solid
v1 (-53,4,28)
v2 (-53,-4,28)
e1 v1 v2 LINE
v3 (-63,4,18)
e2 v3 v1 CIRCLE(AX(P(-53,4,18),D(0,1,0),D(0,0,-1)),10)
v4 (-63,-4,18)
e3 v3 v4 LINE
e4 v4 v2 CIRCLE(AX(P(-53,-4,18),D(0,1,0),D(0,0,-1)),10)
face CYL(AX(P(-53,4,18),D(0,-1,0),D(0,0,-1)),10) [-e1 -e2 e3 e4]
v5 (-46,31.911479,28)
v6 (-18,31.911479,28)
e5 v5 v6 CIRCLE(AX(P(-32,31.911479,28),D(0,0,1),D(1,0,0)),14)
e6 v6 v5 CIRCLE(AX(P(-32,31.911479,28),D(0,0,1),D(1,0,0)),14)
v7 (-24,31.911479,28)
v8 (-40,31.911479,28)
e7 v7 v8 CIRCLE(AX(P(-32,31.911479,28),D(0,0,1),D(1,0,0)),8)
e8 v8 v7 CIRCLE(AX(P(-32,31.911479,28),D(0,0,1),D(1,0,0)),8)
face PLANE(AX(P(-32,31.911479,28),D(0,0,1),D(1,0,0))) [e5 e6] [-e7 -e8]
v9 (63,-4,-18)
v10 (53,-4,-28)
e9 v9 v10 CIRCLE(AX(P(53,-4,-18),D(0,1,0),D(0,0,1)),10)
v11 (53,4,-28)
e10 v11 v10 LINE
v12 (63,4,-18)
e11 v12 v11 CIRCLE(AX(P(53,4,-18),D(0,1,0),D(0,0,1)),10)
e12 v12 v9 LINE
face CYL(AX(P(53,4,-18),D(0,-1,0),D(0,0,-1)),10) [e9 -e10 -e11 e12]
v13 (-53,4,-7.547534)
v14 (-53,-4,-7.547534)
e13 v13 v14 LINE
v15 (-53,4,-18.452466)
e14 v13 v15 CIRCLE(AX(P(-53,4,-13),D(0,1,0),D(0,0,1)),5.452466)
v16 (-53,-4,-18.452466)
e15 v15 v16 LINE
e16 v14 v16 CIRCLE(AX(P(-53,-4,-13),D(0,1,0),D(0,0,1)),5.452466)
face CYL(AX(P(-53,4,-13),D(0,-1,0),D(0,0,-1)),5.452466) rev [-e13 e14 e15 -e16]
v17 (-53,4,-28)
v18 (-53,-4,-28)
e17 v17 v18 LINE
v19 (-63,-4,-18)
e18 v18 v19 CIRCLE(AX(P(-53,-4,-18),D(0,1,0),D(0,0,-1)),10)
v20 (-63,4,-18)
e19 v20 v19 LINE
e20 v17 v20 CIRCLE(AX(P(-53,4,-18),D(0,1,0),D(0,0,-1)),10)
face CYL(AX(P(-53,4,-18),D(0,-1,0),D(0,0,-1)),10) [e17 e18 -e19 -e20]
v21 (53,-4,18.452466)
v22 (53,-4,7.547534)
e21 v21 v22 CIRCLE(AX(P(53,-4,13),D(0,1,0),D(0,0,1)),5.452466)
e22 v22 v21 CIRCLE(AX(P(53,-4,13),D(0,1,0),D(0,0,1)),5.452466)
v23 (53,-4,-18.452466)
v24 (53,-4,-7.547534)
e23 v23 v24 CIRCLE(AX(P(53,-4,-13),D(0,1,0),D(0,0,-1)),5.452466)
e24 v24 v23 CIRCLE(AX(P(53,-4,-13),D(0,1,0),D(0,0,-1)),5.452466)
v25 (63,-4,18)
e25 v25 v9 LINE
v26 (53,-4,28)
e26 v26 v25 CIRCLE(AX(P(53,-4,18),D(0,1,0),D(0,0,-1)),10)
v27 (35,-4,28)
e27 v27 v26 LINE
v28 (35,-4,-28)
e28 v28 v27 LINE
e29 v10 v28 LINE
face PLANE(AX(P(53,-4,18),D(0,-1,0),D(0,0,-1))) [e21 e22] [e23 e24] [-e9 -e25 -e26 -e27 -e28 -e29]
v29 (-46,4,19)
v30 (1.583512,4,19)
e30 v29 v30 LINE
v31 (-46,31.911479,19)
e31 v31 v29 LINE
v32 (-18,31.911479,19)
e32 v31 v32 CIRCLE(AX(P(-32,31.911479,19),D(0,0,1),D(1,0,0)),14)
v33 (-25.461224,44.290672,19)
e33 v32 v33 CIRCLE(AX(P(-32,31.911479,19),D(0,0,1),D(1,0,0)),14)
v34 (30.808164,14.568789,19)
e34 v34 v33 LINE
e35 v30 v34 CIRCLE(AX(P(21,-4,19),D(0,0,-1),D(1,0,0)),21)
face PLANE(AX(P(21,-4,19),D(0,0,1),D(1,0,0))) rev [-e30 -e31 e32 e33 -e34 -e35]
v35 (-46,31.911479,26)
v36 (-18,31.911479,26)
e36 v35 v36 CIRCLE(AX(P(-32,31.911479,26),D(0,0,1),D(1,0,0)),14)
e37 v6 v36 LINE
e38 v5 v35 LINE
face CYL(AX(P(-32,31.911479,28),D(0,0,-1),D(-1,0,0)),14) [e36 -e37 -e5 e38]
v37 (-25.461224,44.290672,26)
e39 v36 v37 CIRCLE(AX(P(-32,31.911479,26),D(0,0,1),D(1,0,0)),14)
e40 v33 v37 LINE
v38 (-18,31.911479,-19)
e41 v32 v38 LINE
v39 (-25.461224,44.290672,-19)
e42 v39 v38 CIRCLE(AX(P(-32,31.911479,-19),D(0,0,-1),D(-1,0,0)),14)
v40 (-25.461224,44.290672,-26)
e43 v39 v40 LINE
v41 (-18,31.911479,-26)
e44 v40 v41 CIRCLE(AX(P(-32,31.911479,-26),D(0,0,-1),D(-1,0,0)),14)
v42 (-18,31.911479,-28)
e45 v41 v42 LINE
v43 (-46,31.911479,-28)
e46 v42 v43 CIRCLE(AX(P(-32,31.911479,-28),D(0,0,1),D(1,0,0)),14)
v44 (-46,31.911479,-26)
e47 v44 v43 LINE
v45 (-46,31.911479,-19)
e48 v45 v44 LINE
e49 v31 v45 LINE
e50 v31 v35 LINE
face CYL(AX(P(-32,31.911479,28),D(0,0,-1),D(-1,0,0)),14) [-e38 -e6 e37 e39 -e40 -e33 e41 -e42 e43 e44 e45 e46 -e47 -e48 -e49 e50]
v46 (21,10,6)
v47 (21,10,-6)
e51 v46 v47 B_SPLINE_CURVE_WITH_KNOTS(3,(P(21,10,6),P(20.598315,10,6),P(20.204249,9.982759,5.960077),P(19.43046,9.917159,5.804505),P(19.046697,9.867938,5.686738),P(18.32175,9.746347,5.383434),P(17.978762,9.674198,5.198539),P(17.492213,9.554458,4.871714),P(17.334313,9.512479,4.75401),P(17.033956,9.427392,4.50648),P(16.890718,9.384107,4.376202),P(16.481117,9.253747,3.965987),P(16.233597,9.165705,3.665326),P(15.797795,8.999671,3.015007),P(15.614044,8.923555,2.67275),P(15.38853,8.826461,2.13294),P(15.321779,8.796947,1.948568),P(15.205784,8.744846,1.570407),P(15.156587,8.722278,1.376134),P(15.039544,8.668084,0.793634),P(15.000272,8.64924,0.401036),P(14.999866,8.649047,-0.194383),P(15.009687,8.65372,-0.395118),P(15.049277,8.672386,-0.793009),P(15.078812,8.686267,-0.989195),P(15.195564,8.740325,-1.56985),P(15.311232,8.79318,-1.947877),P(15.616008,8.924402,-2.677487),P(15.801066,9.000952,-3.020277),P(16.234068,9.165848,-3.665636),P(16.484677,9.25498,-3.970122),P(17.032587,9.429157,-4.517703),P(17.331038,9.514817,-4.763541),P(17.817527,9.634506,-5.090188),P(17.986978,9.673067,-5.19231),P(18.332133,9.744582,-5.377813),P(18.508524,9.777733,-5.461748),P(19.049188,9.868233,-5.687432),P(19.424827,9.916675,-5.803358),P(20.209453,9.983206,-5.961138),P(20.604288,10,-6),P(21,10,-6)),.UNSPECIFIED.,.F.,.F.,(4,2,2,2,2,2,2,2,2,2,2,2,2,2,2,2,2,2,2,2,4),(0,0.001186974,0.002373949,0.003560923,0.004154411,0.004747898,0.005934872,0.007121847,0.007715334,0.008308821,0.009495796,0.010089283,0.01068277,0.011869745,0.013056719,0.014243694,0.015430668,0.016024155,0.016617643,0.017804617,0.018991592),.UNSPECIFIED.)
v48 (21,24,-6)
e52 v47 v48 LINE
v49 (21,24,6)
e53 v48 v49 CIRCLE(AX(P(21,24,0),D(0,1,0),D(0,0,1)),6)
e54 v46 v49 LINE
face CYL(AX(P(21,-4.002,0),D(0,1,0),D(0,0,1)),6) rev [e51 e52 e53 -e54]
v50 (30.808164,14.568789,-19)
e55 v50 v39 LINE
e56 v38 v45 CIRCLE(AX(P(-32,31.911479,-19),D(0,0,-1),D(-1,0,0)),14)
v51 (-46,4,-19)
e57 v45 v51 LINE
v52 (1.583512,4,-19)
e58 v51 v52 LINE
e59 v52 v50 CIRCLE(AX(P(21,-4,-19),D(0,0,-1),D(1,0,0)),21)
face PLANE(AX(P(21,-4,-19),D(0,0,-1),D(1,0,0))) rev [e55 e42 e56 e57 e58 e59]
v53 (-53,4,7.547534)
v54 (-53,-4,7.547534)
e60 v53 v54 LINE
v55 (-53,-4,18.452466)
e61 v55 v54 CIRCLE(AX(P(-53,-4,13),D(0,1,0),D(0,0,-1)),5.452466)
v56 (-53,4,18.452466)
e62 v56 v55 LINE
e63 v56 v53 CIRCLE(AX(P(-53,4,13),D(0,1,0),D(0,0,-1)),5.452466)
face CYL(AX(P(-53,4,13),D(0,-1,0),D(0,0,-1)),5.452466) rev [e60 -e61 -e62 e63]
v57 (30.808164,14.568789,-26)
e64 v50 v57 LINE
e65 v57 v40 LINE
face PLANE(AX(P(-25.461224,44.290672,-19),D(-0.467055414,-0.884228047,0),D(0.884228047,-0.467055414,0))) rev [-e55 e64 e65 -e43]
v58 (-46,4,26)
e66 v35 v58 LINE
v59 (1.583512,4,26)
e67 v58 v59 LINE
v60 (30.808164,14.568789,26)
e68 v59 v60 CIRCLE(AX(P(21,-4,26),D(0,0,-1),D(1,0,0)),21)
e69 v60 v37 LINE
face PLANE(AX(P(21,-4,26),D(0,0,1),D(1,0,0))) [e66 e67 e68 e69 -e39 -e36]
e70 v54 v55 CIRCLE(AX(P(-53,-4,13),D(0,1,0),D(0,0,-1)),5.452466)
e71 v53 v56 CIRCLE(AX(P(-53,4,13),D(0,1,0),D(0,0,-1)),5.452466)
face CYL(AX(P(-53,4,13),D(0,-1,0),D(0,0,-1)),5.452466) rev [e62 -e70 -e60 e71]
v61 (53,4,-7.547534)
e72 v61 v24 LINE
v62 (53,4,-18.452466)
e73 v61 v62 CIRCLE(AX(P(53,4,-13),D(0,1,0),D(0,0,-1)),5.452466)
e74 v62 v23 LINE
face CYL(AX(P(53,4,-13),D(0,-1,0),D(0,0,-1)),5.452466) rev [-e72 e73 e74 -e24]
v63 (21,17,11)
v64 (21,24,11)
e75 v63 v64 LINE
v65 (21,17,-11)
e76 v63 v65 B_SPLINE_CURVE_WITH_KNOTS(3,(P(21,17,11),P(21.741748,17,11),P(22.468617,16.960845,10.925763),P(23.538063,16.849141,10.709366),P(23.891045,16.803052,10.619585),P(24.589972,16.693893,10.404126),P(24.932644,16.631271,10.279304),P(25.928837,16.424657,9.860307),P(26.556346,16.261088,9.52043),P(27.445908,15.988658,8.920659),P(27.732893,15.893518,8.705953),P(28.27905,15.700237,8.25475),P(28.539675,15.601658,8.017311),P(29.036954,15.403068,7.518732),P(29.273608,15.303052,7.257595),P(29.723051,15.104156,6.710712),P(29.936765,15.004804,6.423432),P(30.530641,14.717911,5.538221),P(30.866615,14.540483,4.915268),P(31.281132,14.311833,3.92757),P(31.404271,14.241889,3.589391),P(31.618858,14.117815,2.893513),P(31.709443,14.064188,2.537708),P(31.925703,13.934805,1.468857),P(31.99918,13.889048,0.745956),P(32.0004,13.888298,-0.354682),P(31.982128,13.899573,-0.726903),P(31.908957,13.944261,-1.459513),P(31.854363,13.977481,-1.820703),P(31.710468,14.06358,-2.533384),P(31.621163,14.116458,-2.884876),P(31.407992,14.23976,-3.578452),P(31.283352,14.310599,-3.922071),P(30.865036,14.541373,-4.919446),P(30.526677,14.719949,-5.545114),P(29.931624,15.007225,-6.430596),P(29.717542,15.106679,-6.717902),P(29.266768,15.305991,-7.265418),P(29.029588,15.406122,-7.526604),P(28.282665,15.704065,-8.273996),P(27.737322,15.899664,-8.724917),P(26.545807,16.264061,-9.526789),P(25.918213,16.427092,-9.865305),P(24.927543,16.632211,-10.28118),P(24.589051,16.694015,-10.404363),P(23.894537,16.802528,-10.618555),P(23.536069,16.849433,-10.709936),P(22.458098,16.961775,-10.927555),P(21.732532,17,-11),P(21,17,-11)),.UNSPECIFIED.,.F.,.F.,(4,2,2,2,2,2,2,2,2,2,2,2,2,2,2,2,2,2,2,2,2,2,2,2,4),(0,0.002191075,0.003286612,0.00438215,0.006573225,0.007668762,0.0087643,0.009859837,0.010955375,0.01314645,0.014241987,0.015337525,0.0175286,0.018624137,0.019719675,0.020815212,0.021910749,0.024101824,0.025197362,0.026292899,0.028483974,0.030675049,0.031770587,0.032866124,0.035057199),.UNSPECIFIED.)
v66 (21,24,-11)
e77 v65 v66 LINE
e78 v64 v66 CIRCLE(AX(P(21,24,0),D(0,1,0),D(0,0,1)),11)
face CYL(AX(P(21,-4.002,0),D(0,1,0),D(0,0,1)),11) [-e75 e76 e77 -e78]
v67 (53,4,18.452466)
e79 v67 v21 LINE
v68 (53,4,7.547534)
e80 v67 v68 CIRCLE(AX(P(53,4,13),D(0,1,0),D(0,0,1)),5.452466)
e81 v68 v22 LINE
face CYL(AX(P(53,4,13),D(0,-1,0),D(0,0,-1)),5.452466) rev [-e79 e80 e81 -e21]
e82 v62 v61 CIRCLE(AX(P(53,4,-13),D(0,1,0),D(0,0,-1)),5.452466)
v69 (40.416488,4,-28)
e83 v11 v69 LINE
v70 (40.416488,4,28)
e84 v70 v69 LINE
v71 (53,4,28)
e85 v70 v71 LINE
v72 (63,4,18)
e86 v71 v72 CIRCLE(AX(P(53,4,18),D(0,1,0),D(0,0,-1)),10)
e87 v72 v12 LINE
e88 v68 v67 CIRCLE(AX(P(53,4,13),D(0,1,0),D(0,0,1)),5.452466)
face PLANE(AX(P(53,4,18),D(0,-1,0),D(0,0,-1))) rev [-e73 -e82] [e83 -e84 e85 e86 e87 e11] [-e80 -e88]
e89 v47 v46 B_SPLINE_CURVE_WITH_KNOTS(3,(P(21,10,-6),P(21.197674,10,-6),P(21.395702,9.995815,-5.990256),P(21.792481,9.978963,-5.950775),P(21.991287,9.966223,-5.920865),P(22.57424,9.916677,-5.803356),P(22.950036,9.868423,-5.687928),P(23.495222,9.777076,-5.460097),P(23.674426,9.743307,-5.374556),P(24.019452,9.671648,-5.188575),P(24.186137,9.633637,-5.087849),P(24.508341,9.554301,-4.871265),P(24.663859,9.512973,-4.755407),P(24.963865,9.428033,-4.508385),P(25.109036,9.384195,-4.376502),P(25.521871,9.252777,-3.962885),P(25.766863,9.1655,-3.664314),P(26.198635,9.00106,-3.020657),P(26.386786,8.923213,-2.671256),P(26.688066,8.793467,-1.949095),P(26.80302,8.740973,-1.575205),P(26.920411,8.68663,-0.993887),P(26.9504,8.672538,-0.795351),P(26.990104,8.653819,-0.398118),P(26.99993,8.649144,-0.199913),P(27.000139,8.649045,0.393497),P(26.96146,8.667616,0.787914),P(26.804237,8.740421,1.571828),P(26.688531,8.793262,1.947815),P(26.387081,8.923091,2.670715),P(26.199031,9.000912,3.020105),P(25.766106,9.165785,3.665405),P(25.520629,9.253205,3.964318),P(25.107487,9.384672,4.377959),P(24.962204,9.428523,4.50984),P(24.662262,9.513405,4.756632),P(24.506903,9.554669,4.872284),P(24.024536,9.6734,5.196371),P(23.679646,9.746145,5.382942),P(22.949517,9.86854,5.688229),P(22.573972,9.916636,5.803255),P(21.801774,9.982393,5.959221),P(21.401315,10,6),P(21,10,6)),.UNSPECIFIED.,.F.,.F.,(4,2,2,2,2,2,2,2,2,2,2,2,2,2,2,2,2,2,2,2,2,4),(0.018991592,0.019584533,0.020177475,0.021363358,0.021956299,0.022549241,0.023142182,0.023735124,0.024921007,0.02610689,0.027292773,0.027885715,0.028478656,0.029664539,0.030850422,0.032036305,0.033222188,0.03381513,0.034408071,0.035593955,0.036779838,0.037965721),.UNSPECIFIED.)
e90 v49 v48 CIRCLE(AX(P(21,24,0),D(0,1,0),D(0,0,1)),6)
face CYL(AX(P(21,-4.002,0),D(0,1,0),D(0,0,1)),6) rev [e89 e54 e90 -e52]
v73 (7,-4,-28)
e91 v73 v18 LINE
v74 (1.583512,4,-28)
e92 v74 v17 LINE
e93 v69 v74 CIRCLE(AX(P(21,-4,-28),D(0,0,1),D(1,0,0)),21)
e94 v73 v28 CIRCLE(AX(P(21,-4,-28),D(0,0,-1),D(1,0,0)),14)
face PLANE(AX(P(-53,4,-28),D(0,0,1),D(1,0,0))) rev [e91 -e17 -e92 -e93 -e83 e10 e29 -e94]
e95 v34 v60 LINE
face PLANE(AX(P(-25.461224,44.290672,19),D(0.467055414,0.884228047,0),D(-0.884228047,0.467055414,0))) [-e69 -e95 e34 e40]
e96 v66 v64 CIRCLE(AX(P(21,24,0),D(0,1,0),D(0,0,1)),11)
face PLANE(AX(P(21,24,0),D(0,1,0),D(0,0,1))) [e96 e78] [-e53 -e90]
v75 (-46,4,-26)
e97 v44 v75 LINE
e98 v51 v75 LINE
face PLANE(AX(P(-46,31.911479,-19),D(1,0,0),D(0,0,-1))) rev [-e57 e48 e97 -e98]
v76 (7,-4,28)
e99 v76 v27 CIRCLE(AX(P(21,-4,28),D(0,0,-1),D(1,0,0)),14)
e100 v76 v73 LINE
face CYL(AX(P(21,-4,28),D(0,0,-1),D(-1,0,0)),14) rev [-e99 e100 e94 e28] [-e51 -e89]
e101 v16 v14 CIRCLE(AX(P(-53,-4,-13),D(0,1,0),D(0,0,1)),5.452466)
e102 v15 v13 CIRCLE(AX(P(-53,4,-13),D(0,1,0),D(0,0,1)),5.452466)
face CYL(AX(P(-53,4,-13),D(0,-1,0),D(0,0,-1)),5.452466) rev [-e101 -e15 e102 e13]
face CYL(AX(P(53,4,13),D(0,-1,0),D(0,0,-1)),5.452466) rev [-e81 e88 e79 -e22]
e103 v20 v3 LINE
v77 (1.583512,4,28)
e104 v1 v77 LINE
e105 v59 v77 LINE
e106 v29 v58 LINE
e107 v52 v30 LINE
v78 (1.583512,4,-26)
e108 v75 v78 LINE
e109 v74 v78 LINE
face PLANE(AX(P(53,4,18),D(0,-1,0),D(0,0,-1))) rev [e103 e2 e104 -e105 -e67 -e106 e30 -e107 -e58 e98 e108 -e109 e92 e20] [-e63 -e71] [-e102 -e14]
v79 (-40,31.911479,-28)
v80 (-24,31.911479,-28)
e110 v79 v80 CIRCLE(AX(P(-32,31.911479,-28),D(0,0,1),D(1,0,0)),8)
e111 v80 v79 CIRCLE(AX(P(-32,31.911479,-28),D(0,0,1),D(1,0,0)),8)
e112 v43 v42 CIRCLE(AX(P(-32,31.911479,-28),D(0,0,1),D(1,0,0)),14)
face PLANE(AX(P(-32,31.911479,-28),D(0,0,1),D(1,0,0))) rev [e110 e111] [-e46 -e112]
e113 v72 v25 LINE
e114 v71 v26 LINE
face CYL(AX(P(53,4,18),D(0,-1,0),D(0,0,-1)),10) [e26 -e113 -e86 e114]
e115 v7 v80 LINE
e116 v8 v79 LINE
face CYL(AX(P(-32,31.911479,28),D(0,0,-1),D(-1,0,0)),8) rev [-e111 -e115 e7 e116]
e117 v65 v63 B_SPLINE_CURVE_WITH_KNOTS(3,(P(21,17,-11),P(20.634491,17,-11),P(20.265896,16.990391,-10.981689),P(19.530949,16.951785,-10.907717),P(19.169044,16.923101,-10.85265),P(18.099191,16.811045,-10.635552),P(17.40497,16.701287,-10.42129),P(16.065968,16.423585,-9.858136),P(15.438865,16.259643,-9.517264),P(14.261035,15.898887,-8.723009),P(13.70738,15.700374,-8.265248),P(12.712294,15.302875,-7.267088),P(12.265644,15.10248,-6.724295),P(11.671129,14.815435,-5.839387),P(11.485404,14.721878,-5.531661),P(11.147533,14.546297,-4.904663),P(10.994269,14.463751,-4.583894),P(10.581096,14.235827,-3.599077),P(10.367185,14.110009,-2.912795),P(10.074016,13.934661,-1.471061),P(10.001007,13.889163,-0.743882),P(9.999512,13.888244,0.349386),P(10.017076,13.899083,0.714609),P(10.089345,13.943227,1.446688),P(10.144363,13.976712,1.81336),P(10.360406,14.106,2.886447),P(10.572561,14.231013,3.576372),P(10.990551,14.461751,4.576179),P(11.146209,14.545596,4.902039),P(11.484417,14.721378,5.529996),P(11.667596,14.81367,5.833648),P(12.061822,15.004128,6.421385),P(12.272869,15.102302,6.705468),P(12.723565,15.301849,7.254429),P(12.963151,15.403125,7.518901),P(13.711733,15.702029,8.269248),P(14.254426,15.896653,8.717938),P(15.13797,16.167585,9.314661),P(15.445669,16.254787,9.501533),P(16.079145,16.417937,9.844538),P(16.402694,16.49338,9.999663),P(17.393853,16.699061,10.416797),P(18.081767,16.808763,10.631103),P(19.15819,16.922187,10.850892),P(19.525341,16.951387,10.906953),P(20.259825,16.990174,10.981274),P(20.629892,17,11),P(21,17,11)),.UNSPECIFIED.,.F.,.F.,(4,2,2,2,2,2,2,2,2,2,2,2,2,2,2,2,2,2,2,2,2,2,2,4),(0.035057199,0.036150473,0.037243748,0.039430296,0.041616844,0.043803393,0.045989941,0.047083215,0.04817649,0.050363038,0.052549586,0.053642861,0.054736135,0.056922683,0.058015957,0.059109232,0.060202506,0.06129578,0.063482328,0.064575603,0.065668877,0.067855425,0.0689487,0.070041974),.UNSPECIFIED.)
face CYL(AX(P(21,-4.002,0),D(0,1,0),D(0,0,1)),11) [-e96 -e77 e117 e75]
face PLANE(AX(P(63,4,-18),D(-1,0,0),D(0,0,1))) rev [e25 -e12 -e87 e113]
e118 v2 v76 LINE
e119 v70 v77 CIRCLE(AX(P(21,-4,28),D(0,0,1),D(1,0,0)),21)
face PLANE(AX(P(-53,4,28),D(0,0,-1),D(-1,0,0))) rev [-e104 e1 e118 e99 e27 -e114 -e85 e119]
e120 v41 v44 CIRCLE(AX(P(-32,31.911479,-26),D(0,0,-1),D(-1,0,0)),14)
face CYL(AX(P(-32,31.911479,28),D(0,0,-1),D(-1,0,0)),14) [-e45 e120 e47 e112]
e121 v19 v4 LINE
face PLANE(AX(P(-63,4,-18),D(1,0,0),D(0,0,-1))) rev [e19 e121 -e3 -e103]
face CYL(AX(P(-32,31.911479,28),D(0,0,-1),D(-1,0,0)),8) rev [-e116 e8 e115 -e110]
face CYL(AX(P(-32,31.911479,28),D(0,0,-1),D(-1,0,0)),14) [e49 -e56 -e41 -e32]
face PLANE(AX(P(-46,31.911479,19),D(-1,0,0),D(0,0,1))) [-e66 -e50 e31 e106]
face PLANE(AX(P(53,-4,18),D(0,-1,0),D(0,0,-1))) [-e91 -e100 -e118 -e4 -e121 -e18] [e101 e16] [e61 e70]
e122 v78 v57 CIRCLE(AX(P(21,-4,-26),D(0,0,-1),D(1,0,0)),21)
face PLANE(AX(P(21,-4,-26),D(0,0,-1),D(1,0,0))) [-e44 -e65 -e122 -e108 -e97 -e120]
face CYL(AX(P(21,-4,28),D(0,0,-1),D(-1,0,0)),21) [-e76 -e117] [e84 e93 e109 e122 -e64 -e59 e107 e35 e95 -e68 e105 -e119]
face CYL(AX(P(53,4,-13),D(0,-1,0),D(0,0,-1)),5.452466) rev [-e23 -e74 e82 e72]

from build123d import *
from build123d.topology import SkipClean

# Parameters (mm, degrees)
BASE_PLATE_SKETCH_R      = 5.452465884
BASE_PLATE_DEPTH         = 4
PIVOT_HOUSING_SKETCH_R   = 14
PIVOT_HOUSING_SKETCH_R_2 = 8
PIVOT_HOUSING_DEPTH      = 28
SADDLE_CUT_SKETCH_R      = 14
SADDLE_CUT_28_DEPTH      = 28
SIDE_WEB_SKETCH_R        = 8
SIDE_WEB_DEPTH           = 7
TOP_BOSS_22_REACH        = 76.411
TOP_BOSS_22_END_RADIUS   = 21
TOP_BOSS_SKETCH_R        = 11
TOP_BOSS_SKETCH_R_2      = 6
TOP_BOSS_HOLE_CUT_REACH  = 76.411
TOP_BOSS_HOLE_SKETCH_R   = 6


with BuildPart() as part:
    # Base Plate Sketch → Base Plate (new, symmetric)
    with BuildSketch(Plane(origin=(0, 0, 0), x_dir=(1, 0, 0), z_dir=(0, 1, 0))):
        with BuildLine():
            Line((-53, 28), (53, 28))
            ThreePointArc((53, 28), (60.071067812, 25.071067812), (63, 18))
            Line((63, 18), (63, -18))
            ThreePointArc((63, -18), (60.071067812, -25.071067812), (53, -28))
            Line((53, -28), (-53, -28))
            ThreePointArc((-53, -28), (-60.071067812, -25.071067812), (-63, -18))
            Line((-63, -18), (-63, 18))
            ThreePointArc((-63, 18), (-60.071067812, 25.071067812), (-53, 28))
        make_face()
        with Locations(Location((-53, 13, 0), (0, 0, 270))):
            Circle(BASE_PLATE_SKETCH_R, mode=Mode.SUBTRACT)
        with Locations(Location((-53, -13, 0), (0, 0, 90))):
            Circle(BASE_PLATE_SKETCH_R, mode=Mode.SUBTRACT)
        with Locations(Location((53, -13, 0), (0, 0, 270))):
            Circle(BASE_PLATE_SKETCH_R, mode=Mode.SUBTRACT)
        with Locations(Location((53, 13, 0), (0, 0, 90))):
            Circle(BASE_PLATE_SKETCH_R, mode=Mode.SUBTRACT)
    extrude(amount=BASE_PLATE_DEPTH, both=True)

    # Pivot Housing Sketch → Pivot Housing (add, symmetric)
    # profile 1 of 2: a face of its own
    with BuildSketch(Plane.XY):
        with Locations((-32, 31.911479001)):
            Circle(PIVOT_HOUSING_SKETCH_R)
        with Locations((-32, 31.911479001)):
            Circle(PIVOT_HOUSING_SKETCH_R_2, mode=Mode.SUBTRACT)
    # profile 2 of 2: a face of its own
    with BuildSketch(Plane.XY):
        with BuildLine():
            Line((0, -4), (7, -4))
            ThreePointArc((7, -4), (21, 10), (35, -4))
            Line((35, -4), (42, -4))
            ThreePointArc((42, -4), (21, 17), (0, -4))
        make_face()
    extrude(amount=PIVOT_HOUSING_DEPTH, both=True)


with BuildPart() as pivot_housing_piece_1:
    # of the separate pieces the step leaves, piece 1, a body of its own (pivot_housing_pieces)
    add(part.part.solids().sort_by_distance((-53, -4, -28))[0])

    # Saddle Cut Sketch → Saddle Cut Ø28 (cut, symmetric)
    with SkipClean():  # the faces are left unmerged after this step: merging them gives an invalid solid
        with BuildSketch(Plane.XY):
            with Locations((21, -4)):
                Circle(SADDLE_CUT_SKETCH_R)
        extrude(amount=SADDLE_CUT_28_DEPTH, both=True, mode=Mode.SUBTRACT)



with BuildPart() as pivot_housing_piece_2:
    # of the separate pieces the step leaves, piece 2, a body of its own (pivot_housing_pieces)
    add(part.part.solids().sort_by_distance((-18, 31.911479001, -28))[0])


with BuildPart() as pivot_housing_piece_1_1:
    with SkipClean():  # the faces are left unmerged after this step: merging them gives an invalid solid
        add(pivot_housing_piece_1.part)

        add(pivot_housing_piece_2.part)  # Side Web merges Pivot Housing piece 2
        # Side Web Sketch → Side Web (add)
        with BuildSketch(Plane.XY.offset(26)):
            with BuildLine():
                Line((-46, 4), (1.583512161, 4))
                ThreePointArc((1.583512161, 4), (13.858235624, 15.748296169), (30.808163701, 14.568788997))
                Line((30.808163701, 14.568788997), (-25.4612242, 44.290671665))
                ThreePointArc((-25.4612242, 44.290671665), (-39.22693361, 43.901951494), (-46, 31.911479001))
                Line((-46, 31.911479001), (-46, 4))
            make_face()
            with Locations((-32, 31.911479001)):
                Circle(SIDE_WEB_SKETCH_R, mode=Mode.SUBTRACT)
        side_web = extrude(amount=-SIDE_WEB_DEPTH)

    # Side Web Mirror: Side Web across plane
    with SkipClean():  # the faces are left unmerged after this step: merging them gives an invalid solid
        add(side_web.mirror(Plane.XY))

    # Top Boss Ø22: up to this cylinder (the profile starts outside it)
    with SkipClean():  # the faces are left unmerged after this step: merging them gives an invalid solid
        top_boss_22_end = Plane(origin=(21, -4, -10.688873), z_dir=(0, 0, -1)) * Cylinder(TOP_BOSS_22_END_RADIUS, 195.822, mode=Mode.PRIVATE)
        # Top Boss Sketch → Top Boss Ø22 (add, up to the surface)
        with BuildSketch(Plane(origin=(0, 24, 0), x_dir=(1, 0, 0), z_dir=(0, 1, 0)), mode=Mode.PRIVATE) as top_boss_22_sk1:
            with Locations(Location((21, 0, 0), (0, 0, 270))):
                Circle(TOP_BOSS_SKETCH_R)
            with Locations(Location((21, 0, 0), (0, 0, 270))):
                Circle(TOP_BOSS_SKETCH_R_2, mode=Mode.SUBTRACT)
        top_boss_22_tool1 = extrude(top_boss_22_sk1.sketch, amount=-TOP_BOSS_22_REACH, mode=Mode.PRIVATE) - top_boss_22_end
        add(top_boss_22_tool1.solids().sort_by_distance((21, 24, -10.688873))[0])

    # Top Boss Hole Sketch → Top Boss Hole Cut (cut, up to next)
    with BuildSketch(Plane(origin=(0, 24, 0), x_dir=(1, 0, 0), z_dir=(0, 1, 0)), mode=Mode.PRIVATE) as top_boss_hole_cut_sk1:
        with Locations(Location((21, 0, 0), (0, 0, 270))):
            Circle(TOP_BOSS_HOLE_SKETCH_R)
    top_boss_hole_cut_tool1 = extrude(top_boss_hole_cut_sk1.sketch, amount=-TOP_BOSS_HOLE_CUT_REACH, mode=Mode.PRIVATE) & pivot_housing_piece_1_1.part
    add(top_boss_hole_cut_tool1.solids().sort_by_distance((21, 24, 0))[0], mode=Mode.SUBTRACT)


solid = pivot_housing_piece_1_1.part
